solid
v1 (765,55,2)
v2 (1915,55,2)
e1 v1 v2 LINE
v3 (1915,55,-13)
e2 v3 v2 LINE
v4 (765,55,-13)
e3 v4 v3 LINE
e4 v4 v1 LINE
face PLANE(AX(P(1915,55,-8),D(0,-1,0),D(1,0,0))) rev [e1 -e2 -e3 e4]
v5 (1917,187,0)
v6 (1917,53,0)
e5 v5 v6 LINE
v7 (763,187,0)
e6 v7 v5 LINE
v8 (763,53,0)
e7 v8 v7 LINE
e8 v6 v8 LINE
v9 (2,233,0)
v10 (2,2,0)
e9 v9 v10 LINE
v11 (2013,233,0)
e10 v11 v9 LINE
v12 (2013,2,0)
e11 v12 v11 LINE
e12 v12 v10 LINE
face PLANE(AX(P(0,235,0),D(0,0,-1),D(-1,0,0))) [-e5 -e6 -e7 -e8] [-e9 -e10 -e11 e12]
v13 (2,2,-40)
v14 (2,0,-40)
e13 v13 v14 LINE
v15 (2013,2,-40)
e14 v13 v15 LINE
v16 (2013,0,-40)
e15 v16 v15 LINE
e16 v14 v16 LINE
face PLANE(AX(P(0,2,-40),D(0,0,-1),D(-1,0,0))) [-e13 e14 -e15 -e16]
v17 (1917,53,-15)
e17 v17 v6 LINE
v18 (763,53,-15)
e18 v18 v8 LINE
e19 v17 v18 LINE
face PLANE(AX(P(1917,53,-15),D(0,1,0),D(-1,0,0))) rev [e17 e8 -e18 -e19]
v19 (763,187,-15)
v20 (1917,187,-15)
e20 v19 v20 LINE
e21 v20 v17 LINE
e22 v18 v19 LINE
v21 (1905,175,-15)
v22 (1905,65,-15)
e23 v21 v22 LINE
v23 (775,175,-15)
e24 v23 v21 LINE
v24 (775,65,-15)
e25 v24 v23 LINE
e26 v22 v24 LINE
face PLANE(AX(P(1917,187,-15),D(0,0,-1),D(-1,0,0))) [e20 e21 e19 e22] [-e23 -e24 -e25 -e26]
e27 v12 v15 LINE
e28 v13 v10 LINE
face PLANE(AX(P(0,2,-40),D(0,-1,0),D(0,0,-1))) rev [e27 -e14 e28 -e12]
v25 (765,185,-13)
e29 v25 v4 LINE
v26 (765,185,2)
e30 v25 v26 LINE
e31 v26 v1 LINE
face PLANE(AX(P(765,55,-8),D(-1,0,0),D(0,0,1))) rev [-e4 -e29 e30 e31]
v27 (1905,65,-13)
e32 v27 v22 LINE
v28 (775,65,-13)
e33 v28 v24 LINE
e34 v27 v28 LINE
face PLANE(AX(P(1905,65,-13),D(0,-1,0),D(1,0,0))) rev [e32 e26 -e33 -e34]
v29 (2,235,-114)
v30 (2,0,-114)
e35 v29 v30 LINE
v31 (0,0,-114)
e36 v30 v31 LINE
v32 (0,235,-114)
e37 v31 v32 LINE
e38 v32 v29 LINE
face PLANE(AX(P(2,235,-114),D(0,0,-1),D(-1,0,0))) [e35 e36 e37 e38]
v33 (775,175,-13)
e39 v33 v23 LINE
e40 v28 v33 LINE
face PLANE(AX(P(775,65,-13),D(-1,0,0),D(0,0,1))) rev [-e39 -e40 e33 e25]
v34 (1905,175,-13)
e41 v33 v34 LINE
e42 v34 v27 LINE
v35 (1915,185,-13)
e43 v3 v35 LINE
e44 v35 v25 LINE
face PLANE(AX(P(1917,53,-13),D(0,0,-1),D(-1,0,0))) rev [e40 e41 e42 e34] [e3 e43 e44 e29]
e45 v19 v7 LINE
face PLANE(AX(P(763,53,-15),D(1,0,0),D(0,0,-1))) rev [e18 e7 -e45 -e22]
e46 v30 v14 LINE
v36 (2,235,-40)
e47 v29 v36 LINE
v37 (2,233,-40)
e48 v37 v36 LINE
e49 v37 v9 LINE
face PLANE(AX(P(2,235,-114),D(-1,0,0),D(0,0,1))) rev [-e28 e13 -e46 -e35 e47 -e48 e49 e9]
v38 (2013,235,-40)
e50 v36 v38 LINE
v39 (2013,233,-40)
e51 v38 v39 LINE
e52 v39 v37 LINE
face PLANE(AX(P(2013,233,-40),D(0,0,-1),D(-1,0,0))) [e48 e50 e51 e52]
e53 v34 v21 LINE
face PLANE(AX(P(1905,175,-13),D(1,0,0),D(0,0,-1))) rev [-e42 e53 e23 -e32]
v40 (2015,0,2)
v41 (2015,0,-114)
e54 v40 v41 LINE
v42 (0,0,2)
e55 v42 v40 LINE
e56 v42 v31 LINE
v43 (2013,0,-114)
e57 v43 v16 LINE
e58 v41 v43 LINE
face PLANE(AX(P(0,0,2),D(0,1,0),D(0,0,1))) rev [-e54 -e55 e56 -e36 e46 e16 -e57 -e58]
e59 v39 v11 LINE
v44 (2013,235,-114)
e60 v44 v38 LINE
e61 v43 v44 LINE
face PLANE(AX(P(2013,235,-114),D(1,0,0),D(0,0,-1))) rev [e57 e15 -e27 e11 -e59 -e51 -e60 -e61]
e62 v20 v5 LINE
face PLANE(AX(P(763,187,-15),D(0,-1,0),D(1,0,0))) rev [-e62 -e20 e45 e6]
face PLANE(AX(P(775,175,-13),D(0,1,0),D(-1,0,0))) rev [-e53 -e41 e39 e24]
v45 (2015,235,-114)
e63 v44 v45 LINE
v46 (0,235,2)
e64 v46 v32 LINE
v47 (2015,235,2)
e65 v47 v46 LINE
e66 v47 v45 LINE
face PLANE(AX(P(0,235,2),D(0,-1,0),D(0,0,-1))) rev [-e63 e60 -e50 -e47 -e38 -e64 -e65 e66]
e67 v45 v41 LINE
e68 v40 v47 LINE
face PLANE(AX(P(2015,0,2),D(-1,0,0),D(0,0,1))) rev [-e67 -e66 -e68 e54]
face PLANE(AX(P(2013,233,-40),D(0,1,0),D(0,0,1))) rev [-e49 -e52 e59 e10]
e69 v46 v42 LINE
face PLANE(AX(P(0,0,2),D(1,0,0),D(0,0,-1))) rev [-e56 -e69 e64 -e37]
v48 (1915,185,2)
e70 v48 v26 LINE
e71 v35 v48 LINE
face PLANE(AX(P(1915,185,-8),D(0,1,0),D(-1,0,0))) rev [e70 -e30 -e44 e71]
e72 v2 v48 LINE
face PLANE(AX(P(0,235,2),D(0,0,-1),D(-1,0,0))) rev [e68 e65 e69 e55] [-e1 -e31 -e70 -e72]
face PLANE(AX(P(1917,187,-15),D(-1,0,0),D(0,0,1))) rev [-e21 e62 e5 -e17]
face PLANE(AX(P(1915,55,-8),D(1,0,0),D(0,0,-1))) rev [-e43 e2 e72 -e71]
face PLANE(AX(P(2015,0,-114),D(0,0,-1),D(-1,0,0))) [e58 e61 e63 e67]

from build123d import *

# Parameters (mm, degrees)
SKETCH_2_W          = 2015
SKETCH_2_H          = 235
EXTRUDE_1_DEPTH     = 2
SKETCH_3_W          = 2
SKETCH_3_H          = 235
EXTRUDE_2_DEPTH     = 114
SKETCH_4_W          = 2011
SKETCH_4_H          = 2
EXTRUDE_3_DEPTH     = 40
SKETCH_5_W          = 1150
SKETCH_5_H          = 130
CUT_EXTRUDE_1_DEPTH = 10
SKETCH_6_W          = 2015
SKETCH_6_H          = 42
EXTRUDE_4_DEPTH     = 2
SKETCH_7_W          = 1154
SKETCH_7_H          = 134
SKETCH_7_W_2        = 1150
SKETCH_7_H_2        = 130
EXTRUDE_5_DEPTH     = 15
SKETCH_8_W          = 1154
SKETCH_8_H          = 134
SKETCH_8_W_2        = 1130
SKETCH_8_H_2        = 110
EXTRUDE_6_DEPTH     = 2


with BuildPart() as part:
    # 草图2 → 凸台-拉伸1 (new body)
    with BuildSketch(Plane.XY):
        with Locations((1007.5, 117.5)):
            Rectangle(SKETCH_2_W, SKETCH_2_H)
    extrude(amount=EXTRUDE_1_DEPTH)

    # 草图3 → 凸台-拉伸2 (add)
    with BuildSketch(Plane(origin=(0, 0, 0), x_dir=(-1, 0, 0), z_dir=(0, 0, -1))):
        with Locations((-2014, 117.5)):
            Rectangle(SKETCH_3_W, SKETCH_3_H)
        with Locations((-1, 117.5)):
            Rectangle(SKETCH_3_W, SKETCH_3_H)
    extrude(amount=EXTRUDE_2_DEPTH)

    # 草图4 → 凸台-拉伸3 (add)
    with BuildSketch(Plane(origin=(0, 0, 0), x_dir=(-1, 0, 0), z_dir=(0, 0, -1))):
        with Locations((-1007.5, 234)):
            Rectangle(SKETCH_4_W, SKETCH_4_H)
    extrude(amount=EXTRUDE_3_DEPTH)

    # 草图5 → 切除-拉伸1 (cut)
    with BuildSketch(Plane.XY.offset(2)):
        with Locations((1340, 120)):
            Rectangle(SKETCH_5_W, SKETCH_5_H)
    extrude(amount=-CUT_EXTRUDE_1_DEPTH, mode=Mode.SUBTRACT)

    # 草图6 → 凸台-拉伸4 (add)
    with BuildSketch(Plane.XZ):
        with Locations((1007.5, -19)):
            Rectangle(SKETCH_6_W, SKETCH_6_H)
    extrude(amount=-EXTRUDE_4_DEPTH)

    # 草图7 → 凸台-拉伸5 (add)
    with BuildSketch(Plane(origin=(0, 0, 0), x_dir=(-1, 0, 0), z_dir=(0, 0, -1))):
        with Locations((-1340, 120)):
            Rectangle(SKETCH_7_W, SKETCH_7_H)
        with Locations((-1340, 120)):
            Rectangle(SKETCH_7_W_2, SKETCH_7_H_2, mode=Mode.SUBTRACT)
    extrude(amount=EXTRUDE_5_DEPTH)

    # 草图8 → 凸台-拉伸6 (add)
    with BuildSketch(Plane(origin=(0, 0, -15), x_dir=(-1, 0, 0), z_dir=(0, 0, -1))):
        with Locations((-1340, 120)):
            Rectangle(SKETCH_8_W, SKETCH_8_H)
        with Locations((-1340, 120)):
            Rectangle(SKETCH_8_W_2, SKETCH_8_H_2, mode=Mode.SUBTRACT)
    extrude(amount=-EXTRUDE_6_DEPTH)


solid = part.part
